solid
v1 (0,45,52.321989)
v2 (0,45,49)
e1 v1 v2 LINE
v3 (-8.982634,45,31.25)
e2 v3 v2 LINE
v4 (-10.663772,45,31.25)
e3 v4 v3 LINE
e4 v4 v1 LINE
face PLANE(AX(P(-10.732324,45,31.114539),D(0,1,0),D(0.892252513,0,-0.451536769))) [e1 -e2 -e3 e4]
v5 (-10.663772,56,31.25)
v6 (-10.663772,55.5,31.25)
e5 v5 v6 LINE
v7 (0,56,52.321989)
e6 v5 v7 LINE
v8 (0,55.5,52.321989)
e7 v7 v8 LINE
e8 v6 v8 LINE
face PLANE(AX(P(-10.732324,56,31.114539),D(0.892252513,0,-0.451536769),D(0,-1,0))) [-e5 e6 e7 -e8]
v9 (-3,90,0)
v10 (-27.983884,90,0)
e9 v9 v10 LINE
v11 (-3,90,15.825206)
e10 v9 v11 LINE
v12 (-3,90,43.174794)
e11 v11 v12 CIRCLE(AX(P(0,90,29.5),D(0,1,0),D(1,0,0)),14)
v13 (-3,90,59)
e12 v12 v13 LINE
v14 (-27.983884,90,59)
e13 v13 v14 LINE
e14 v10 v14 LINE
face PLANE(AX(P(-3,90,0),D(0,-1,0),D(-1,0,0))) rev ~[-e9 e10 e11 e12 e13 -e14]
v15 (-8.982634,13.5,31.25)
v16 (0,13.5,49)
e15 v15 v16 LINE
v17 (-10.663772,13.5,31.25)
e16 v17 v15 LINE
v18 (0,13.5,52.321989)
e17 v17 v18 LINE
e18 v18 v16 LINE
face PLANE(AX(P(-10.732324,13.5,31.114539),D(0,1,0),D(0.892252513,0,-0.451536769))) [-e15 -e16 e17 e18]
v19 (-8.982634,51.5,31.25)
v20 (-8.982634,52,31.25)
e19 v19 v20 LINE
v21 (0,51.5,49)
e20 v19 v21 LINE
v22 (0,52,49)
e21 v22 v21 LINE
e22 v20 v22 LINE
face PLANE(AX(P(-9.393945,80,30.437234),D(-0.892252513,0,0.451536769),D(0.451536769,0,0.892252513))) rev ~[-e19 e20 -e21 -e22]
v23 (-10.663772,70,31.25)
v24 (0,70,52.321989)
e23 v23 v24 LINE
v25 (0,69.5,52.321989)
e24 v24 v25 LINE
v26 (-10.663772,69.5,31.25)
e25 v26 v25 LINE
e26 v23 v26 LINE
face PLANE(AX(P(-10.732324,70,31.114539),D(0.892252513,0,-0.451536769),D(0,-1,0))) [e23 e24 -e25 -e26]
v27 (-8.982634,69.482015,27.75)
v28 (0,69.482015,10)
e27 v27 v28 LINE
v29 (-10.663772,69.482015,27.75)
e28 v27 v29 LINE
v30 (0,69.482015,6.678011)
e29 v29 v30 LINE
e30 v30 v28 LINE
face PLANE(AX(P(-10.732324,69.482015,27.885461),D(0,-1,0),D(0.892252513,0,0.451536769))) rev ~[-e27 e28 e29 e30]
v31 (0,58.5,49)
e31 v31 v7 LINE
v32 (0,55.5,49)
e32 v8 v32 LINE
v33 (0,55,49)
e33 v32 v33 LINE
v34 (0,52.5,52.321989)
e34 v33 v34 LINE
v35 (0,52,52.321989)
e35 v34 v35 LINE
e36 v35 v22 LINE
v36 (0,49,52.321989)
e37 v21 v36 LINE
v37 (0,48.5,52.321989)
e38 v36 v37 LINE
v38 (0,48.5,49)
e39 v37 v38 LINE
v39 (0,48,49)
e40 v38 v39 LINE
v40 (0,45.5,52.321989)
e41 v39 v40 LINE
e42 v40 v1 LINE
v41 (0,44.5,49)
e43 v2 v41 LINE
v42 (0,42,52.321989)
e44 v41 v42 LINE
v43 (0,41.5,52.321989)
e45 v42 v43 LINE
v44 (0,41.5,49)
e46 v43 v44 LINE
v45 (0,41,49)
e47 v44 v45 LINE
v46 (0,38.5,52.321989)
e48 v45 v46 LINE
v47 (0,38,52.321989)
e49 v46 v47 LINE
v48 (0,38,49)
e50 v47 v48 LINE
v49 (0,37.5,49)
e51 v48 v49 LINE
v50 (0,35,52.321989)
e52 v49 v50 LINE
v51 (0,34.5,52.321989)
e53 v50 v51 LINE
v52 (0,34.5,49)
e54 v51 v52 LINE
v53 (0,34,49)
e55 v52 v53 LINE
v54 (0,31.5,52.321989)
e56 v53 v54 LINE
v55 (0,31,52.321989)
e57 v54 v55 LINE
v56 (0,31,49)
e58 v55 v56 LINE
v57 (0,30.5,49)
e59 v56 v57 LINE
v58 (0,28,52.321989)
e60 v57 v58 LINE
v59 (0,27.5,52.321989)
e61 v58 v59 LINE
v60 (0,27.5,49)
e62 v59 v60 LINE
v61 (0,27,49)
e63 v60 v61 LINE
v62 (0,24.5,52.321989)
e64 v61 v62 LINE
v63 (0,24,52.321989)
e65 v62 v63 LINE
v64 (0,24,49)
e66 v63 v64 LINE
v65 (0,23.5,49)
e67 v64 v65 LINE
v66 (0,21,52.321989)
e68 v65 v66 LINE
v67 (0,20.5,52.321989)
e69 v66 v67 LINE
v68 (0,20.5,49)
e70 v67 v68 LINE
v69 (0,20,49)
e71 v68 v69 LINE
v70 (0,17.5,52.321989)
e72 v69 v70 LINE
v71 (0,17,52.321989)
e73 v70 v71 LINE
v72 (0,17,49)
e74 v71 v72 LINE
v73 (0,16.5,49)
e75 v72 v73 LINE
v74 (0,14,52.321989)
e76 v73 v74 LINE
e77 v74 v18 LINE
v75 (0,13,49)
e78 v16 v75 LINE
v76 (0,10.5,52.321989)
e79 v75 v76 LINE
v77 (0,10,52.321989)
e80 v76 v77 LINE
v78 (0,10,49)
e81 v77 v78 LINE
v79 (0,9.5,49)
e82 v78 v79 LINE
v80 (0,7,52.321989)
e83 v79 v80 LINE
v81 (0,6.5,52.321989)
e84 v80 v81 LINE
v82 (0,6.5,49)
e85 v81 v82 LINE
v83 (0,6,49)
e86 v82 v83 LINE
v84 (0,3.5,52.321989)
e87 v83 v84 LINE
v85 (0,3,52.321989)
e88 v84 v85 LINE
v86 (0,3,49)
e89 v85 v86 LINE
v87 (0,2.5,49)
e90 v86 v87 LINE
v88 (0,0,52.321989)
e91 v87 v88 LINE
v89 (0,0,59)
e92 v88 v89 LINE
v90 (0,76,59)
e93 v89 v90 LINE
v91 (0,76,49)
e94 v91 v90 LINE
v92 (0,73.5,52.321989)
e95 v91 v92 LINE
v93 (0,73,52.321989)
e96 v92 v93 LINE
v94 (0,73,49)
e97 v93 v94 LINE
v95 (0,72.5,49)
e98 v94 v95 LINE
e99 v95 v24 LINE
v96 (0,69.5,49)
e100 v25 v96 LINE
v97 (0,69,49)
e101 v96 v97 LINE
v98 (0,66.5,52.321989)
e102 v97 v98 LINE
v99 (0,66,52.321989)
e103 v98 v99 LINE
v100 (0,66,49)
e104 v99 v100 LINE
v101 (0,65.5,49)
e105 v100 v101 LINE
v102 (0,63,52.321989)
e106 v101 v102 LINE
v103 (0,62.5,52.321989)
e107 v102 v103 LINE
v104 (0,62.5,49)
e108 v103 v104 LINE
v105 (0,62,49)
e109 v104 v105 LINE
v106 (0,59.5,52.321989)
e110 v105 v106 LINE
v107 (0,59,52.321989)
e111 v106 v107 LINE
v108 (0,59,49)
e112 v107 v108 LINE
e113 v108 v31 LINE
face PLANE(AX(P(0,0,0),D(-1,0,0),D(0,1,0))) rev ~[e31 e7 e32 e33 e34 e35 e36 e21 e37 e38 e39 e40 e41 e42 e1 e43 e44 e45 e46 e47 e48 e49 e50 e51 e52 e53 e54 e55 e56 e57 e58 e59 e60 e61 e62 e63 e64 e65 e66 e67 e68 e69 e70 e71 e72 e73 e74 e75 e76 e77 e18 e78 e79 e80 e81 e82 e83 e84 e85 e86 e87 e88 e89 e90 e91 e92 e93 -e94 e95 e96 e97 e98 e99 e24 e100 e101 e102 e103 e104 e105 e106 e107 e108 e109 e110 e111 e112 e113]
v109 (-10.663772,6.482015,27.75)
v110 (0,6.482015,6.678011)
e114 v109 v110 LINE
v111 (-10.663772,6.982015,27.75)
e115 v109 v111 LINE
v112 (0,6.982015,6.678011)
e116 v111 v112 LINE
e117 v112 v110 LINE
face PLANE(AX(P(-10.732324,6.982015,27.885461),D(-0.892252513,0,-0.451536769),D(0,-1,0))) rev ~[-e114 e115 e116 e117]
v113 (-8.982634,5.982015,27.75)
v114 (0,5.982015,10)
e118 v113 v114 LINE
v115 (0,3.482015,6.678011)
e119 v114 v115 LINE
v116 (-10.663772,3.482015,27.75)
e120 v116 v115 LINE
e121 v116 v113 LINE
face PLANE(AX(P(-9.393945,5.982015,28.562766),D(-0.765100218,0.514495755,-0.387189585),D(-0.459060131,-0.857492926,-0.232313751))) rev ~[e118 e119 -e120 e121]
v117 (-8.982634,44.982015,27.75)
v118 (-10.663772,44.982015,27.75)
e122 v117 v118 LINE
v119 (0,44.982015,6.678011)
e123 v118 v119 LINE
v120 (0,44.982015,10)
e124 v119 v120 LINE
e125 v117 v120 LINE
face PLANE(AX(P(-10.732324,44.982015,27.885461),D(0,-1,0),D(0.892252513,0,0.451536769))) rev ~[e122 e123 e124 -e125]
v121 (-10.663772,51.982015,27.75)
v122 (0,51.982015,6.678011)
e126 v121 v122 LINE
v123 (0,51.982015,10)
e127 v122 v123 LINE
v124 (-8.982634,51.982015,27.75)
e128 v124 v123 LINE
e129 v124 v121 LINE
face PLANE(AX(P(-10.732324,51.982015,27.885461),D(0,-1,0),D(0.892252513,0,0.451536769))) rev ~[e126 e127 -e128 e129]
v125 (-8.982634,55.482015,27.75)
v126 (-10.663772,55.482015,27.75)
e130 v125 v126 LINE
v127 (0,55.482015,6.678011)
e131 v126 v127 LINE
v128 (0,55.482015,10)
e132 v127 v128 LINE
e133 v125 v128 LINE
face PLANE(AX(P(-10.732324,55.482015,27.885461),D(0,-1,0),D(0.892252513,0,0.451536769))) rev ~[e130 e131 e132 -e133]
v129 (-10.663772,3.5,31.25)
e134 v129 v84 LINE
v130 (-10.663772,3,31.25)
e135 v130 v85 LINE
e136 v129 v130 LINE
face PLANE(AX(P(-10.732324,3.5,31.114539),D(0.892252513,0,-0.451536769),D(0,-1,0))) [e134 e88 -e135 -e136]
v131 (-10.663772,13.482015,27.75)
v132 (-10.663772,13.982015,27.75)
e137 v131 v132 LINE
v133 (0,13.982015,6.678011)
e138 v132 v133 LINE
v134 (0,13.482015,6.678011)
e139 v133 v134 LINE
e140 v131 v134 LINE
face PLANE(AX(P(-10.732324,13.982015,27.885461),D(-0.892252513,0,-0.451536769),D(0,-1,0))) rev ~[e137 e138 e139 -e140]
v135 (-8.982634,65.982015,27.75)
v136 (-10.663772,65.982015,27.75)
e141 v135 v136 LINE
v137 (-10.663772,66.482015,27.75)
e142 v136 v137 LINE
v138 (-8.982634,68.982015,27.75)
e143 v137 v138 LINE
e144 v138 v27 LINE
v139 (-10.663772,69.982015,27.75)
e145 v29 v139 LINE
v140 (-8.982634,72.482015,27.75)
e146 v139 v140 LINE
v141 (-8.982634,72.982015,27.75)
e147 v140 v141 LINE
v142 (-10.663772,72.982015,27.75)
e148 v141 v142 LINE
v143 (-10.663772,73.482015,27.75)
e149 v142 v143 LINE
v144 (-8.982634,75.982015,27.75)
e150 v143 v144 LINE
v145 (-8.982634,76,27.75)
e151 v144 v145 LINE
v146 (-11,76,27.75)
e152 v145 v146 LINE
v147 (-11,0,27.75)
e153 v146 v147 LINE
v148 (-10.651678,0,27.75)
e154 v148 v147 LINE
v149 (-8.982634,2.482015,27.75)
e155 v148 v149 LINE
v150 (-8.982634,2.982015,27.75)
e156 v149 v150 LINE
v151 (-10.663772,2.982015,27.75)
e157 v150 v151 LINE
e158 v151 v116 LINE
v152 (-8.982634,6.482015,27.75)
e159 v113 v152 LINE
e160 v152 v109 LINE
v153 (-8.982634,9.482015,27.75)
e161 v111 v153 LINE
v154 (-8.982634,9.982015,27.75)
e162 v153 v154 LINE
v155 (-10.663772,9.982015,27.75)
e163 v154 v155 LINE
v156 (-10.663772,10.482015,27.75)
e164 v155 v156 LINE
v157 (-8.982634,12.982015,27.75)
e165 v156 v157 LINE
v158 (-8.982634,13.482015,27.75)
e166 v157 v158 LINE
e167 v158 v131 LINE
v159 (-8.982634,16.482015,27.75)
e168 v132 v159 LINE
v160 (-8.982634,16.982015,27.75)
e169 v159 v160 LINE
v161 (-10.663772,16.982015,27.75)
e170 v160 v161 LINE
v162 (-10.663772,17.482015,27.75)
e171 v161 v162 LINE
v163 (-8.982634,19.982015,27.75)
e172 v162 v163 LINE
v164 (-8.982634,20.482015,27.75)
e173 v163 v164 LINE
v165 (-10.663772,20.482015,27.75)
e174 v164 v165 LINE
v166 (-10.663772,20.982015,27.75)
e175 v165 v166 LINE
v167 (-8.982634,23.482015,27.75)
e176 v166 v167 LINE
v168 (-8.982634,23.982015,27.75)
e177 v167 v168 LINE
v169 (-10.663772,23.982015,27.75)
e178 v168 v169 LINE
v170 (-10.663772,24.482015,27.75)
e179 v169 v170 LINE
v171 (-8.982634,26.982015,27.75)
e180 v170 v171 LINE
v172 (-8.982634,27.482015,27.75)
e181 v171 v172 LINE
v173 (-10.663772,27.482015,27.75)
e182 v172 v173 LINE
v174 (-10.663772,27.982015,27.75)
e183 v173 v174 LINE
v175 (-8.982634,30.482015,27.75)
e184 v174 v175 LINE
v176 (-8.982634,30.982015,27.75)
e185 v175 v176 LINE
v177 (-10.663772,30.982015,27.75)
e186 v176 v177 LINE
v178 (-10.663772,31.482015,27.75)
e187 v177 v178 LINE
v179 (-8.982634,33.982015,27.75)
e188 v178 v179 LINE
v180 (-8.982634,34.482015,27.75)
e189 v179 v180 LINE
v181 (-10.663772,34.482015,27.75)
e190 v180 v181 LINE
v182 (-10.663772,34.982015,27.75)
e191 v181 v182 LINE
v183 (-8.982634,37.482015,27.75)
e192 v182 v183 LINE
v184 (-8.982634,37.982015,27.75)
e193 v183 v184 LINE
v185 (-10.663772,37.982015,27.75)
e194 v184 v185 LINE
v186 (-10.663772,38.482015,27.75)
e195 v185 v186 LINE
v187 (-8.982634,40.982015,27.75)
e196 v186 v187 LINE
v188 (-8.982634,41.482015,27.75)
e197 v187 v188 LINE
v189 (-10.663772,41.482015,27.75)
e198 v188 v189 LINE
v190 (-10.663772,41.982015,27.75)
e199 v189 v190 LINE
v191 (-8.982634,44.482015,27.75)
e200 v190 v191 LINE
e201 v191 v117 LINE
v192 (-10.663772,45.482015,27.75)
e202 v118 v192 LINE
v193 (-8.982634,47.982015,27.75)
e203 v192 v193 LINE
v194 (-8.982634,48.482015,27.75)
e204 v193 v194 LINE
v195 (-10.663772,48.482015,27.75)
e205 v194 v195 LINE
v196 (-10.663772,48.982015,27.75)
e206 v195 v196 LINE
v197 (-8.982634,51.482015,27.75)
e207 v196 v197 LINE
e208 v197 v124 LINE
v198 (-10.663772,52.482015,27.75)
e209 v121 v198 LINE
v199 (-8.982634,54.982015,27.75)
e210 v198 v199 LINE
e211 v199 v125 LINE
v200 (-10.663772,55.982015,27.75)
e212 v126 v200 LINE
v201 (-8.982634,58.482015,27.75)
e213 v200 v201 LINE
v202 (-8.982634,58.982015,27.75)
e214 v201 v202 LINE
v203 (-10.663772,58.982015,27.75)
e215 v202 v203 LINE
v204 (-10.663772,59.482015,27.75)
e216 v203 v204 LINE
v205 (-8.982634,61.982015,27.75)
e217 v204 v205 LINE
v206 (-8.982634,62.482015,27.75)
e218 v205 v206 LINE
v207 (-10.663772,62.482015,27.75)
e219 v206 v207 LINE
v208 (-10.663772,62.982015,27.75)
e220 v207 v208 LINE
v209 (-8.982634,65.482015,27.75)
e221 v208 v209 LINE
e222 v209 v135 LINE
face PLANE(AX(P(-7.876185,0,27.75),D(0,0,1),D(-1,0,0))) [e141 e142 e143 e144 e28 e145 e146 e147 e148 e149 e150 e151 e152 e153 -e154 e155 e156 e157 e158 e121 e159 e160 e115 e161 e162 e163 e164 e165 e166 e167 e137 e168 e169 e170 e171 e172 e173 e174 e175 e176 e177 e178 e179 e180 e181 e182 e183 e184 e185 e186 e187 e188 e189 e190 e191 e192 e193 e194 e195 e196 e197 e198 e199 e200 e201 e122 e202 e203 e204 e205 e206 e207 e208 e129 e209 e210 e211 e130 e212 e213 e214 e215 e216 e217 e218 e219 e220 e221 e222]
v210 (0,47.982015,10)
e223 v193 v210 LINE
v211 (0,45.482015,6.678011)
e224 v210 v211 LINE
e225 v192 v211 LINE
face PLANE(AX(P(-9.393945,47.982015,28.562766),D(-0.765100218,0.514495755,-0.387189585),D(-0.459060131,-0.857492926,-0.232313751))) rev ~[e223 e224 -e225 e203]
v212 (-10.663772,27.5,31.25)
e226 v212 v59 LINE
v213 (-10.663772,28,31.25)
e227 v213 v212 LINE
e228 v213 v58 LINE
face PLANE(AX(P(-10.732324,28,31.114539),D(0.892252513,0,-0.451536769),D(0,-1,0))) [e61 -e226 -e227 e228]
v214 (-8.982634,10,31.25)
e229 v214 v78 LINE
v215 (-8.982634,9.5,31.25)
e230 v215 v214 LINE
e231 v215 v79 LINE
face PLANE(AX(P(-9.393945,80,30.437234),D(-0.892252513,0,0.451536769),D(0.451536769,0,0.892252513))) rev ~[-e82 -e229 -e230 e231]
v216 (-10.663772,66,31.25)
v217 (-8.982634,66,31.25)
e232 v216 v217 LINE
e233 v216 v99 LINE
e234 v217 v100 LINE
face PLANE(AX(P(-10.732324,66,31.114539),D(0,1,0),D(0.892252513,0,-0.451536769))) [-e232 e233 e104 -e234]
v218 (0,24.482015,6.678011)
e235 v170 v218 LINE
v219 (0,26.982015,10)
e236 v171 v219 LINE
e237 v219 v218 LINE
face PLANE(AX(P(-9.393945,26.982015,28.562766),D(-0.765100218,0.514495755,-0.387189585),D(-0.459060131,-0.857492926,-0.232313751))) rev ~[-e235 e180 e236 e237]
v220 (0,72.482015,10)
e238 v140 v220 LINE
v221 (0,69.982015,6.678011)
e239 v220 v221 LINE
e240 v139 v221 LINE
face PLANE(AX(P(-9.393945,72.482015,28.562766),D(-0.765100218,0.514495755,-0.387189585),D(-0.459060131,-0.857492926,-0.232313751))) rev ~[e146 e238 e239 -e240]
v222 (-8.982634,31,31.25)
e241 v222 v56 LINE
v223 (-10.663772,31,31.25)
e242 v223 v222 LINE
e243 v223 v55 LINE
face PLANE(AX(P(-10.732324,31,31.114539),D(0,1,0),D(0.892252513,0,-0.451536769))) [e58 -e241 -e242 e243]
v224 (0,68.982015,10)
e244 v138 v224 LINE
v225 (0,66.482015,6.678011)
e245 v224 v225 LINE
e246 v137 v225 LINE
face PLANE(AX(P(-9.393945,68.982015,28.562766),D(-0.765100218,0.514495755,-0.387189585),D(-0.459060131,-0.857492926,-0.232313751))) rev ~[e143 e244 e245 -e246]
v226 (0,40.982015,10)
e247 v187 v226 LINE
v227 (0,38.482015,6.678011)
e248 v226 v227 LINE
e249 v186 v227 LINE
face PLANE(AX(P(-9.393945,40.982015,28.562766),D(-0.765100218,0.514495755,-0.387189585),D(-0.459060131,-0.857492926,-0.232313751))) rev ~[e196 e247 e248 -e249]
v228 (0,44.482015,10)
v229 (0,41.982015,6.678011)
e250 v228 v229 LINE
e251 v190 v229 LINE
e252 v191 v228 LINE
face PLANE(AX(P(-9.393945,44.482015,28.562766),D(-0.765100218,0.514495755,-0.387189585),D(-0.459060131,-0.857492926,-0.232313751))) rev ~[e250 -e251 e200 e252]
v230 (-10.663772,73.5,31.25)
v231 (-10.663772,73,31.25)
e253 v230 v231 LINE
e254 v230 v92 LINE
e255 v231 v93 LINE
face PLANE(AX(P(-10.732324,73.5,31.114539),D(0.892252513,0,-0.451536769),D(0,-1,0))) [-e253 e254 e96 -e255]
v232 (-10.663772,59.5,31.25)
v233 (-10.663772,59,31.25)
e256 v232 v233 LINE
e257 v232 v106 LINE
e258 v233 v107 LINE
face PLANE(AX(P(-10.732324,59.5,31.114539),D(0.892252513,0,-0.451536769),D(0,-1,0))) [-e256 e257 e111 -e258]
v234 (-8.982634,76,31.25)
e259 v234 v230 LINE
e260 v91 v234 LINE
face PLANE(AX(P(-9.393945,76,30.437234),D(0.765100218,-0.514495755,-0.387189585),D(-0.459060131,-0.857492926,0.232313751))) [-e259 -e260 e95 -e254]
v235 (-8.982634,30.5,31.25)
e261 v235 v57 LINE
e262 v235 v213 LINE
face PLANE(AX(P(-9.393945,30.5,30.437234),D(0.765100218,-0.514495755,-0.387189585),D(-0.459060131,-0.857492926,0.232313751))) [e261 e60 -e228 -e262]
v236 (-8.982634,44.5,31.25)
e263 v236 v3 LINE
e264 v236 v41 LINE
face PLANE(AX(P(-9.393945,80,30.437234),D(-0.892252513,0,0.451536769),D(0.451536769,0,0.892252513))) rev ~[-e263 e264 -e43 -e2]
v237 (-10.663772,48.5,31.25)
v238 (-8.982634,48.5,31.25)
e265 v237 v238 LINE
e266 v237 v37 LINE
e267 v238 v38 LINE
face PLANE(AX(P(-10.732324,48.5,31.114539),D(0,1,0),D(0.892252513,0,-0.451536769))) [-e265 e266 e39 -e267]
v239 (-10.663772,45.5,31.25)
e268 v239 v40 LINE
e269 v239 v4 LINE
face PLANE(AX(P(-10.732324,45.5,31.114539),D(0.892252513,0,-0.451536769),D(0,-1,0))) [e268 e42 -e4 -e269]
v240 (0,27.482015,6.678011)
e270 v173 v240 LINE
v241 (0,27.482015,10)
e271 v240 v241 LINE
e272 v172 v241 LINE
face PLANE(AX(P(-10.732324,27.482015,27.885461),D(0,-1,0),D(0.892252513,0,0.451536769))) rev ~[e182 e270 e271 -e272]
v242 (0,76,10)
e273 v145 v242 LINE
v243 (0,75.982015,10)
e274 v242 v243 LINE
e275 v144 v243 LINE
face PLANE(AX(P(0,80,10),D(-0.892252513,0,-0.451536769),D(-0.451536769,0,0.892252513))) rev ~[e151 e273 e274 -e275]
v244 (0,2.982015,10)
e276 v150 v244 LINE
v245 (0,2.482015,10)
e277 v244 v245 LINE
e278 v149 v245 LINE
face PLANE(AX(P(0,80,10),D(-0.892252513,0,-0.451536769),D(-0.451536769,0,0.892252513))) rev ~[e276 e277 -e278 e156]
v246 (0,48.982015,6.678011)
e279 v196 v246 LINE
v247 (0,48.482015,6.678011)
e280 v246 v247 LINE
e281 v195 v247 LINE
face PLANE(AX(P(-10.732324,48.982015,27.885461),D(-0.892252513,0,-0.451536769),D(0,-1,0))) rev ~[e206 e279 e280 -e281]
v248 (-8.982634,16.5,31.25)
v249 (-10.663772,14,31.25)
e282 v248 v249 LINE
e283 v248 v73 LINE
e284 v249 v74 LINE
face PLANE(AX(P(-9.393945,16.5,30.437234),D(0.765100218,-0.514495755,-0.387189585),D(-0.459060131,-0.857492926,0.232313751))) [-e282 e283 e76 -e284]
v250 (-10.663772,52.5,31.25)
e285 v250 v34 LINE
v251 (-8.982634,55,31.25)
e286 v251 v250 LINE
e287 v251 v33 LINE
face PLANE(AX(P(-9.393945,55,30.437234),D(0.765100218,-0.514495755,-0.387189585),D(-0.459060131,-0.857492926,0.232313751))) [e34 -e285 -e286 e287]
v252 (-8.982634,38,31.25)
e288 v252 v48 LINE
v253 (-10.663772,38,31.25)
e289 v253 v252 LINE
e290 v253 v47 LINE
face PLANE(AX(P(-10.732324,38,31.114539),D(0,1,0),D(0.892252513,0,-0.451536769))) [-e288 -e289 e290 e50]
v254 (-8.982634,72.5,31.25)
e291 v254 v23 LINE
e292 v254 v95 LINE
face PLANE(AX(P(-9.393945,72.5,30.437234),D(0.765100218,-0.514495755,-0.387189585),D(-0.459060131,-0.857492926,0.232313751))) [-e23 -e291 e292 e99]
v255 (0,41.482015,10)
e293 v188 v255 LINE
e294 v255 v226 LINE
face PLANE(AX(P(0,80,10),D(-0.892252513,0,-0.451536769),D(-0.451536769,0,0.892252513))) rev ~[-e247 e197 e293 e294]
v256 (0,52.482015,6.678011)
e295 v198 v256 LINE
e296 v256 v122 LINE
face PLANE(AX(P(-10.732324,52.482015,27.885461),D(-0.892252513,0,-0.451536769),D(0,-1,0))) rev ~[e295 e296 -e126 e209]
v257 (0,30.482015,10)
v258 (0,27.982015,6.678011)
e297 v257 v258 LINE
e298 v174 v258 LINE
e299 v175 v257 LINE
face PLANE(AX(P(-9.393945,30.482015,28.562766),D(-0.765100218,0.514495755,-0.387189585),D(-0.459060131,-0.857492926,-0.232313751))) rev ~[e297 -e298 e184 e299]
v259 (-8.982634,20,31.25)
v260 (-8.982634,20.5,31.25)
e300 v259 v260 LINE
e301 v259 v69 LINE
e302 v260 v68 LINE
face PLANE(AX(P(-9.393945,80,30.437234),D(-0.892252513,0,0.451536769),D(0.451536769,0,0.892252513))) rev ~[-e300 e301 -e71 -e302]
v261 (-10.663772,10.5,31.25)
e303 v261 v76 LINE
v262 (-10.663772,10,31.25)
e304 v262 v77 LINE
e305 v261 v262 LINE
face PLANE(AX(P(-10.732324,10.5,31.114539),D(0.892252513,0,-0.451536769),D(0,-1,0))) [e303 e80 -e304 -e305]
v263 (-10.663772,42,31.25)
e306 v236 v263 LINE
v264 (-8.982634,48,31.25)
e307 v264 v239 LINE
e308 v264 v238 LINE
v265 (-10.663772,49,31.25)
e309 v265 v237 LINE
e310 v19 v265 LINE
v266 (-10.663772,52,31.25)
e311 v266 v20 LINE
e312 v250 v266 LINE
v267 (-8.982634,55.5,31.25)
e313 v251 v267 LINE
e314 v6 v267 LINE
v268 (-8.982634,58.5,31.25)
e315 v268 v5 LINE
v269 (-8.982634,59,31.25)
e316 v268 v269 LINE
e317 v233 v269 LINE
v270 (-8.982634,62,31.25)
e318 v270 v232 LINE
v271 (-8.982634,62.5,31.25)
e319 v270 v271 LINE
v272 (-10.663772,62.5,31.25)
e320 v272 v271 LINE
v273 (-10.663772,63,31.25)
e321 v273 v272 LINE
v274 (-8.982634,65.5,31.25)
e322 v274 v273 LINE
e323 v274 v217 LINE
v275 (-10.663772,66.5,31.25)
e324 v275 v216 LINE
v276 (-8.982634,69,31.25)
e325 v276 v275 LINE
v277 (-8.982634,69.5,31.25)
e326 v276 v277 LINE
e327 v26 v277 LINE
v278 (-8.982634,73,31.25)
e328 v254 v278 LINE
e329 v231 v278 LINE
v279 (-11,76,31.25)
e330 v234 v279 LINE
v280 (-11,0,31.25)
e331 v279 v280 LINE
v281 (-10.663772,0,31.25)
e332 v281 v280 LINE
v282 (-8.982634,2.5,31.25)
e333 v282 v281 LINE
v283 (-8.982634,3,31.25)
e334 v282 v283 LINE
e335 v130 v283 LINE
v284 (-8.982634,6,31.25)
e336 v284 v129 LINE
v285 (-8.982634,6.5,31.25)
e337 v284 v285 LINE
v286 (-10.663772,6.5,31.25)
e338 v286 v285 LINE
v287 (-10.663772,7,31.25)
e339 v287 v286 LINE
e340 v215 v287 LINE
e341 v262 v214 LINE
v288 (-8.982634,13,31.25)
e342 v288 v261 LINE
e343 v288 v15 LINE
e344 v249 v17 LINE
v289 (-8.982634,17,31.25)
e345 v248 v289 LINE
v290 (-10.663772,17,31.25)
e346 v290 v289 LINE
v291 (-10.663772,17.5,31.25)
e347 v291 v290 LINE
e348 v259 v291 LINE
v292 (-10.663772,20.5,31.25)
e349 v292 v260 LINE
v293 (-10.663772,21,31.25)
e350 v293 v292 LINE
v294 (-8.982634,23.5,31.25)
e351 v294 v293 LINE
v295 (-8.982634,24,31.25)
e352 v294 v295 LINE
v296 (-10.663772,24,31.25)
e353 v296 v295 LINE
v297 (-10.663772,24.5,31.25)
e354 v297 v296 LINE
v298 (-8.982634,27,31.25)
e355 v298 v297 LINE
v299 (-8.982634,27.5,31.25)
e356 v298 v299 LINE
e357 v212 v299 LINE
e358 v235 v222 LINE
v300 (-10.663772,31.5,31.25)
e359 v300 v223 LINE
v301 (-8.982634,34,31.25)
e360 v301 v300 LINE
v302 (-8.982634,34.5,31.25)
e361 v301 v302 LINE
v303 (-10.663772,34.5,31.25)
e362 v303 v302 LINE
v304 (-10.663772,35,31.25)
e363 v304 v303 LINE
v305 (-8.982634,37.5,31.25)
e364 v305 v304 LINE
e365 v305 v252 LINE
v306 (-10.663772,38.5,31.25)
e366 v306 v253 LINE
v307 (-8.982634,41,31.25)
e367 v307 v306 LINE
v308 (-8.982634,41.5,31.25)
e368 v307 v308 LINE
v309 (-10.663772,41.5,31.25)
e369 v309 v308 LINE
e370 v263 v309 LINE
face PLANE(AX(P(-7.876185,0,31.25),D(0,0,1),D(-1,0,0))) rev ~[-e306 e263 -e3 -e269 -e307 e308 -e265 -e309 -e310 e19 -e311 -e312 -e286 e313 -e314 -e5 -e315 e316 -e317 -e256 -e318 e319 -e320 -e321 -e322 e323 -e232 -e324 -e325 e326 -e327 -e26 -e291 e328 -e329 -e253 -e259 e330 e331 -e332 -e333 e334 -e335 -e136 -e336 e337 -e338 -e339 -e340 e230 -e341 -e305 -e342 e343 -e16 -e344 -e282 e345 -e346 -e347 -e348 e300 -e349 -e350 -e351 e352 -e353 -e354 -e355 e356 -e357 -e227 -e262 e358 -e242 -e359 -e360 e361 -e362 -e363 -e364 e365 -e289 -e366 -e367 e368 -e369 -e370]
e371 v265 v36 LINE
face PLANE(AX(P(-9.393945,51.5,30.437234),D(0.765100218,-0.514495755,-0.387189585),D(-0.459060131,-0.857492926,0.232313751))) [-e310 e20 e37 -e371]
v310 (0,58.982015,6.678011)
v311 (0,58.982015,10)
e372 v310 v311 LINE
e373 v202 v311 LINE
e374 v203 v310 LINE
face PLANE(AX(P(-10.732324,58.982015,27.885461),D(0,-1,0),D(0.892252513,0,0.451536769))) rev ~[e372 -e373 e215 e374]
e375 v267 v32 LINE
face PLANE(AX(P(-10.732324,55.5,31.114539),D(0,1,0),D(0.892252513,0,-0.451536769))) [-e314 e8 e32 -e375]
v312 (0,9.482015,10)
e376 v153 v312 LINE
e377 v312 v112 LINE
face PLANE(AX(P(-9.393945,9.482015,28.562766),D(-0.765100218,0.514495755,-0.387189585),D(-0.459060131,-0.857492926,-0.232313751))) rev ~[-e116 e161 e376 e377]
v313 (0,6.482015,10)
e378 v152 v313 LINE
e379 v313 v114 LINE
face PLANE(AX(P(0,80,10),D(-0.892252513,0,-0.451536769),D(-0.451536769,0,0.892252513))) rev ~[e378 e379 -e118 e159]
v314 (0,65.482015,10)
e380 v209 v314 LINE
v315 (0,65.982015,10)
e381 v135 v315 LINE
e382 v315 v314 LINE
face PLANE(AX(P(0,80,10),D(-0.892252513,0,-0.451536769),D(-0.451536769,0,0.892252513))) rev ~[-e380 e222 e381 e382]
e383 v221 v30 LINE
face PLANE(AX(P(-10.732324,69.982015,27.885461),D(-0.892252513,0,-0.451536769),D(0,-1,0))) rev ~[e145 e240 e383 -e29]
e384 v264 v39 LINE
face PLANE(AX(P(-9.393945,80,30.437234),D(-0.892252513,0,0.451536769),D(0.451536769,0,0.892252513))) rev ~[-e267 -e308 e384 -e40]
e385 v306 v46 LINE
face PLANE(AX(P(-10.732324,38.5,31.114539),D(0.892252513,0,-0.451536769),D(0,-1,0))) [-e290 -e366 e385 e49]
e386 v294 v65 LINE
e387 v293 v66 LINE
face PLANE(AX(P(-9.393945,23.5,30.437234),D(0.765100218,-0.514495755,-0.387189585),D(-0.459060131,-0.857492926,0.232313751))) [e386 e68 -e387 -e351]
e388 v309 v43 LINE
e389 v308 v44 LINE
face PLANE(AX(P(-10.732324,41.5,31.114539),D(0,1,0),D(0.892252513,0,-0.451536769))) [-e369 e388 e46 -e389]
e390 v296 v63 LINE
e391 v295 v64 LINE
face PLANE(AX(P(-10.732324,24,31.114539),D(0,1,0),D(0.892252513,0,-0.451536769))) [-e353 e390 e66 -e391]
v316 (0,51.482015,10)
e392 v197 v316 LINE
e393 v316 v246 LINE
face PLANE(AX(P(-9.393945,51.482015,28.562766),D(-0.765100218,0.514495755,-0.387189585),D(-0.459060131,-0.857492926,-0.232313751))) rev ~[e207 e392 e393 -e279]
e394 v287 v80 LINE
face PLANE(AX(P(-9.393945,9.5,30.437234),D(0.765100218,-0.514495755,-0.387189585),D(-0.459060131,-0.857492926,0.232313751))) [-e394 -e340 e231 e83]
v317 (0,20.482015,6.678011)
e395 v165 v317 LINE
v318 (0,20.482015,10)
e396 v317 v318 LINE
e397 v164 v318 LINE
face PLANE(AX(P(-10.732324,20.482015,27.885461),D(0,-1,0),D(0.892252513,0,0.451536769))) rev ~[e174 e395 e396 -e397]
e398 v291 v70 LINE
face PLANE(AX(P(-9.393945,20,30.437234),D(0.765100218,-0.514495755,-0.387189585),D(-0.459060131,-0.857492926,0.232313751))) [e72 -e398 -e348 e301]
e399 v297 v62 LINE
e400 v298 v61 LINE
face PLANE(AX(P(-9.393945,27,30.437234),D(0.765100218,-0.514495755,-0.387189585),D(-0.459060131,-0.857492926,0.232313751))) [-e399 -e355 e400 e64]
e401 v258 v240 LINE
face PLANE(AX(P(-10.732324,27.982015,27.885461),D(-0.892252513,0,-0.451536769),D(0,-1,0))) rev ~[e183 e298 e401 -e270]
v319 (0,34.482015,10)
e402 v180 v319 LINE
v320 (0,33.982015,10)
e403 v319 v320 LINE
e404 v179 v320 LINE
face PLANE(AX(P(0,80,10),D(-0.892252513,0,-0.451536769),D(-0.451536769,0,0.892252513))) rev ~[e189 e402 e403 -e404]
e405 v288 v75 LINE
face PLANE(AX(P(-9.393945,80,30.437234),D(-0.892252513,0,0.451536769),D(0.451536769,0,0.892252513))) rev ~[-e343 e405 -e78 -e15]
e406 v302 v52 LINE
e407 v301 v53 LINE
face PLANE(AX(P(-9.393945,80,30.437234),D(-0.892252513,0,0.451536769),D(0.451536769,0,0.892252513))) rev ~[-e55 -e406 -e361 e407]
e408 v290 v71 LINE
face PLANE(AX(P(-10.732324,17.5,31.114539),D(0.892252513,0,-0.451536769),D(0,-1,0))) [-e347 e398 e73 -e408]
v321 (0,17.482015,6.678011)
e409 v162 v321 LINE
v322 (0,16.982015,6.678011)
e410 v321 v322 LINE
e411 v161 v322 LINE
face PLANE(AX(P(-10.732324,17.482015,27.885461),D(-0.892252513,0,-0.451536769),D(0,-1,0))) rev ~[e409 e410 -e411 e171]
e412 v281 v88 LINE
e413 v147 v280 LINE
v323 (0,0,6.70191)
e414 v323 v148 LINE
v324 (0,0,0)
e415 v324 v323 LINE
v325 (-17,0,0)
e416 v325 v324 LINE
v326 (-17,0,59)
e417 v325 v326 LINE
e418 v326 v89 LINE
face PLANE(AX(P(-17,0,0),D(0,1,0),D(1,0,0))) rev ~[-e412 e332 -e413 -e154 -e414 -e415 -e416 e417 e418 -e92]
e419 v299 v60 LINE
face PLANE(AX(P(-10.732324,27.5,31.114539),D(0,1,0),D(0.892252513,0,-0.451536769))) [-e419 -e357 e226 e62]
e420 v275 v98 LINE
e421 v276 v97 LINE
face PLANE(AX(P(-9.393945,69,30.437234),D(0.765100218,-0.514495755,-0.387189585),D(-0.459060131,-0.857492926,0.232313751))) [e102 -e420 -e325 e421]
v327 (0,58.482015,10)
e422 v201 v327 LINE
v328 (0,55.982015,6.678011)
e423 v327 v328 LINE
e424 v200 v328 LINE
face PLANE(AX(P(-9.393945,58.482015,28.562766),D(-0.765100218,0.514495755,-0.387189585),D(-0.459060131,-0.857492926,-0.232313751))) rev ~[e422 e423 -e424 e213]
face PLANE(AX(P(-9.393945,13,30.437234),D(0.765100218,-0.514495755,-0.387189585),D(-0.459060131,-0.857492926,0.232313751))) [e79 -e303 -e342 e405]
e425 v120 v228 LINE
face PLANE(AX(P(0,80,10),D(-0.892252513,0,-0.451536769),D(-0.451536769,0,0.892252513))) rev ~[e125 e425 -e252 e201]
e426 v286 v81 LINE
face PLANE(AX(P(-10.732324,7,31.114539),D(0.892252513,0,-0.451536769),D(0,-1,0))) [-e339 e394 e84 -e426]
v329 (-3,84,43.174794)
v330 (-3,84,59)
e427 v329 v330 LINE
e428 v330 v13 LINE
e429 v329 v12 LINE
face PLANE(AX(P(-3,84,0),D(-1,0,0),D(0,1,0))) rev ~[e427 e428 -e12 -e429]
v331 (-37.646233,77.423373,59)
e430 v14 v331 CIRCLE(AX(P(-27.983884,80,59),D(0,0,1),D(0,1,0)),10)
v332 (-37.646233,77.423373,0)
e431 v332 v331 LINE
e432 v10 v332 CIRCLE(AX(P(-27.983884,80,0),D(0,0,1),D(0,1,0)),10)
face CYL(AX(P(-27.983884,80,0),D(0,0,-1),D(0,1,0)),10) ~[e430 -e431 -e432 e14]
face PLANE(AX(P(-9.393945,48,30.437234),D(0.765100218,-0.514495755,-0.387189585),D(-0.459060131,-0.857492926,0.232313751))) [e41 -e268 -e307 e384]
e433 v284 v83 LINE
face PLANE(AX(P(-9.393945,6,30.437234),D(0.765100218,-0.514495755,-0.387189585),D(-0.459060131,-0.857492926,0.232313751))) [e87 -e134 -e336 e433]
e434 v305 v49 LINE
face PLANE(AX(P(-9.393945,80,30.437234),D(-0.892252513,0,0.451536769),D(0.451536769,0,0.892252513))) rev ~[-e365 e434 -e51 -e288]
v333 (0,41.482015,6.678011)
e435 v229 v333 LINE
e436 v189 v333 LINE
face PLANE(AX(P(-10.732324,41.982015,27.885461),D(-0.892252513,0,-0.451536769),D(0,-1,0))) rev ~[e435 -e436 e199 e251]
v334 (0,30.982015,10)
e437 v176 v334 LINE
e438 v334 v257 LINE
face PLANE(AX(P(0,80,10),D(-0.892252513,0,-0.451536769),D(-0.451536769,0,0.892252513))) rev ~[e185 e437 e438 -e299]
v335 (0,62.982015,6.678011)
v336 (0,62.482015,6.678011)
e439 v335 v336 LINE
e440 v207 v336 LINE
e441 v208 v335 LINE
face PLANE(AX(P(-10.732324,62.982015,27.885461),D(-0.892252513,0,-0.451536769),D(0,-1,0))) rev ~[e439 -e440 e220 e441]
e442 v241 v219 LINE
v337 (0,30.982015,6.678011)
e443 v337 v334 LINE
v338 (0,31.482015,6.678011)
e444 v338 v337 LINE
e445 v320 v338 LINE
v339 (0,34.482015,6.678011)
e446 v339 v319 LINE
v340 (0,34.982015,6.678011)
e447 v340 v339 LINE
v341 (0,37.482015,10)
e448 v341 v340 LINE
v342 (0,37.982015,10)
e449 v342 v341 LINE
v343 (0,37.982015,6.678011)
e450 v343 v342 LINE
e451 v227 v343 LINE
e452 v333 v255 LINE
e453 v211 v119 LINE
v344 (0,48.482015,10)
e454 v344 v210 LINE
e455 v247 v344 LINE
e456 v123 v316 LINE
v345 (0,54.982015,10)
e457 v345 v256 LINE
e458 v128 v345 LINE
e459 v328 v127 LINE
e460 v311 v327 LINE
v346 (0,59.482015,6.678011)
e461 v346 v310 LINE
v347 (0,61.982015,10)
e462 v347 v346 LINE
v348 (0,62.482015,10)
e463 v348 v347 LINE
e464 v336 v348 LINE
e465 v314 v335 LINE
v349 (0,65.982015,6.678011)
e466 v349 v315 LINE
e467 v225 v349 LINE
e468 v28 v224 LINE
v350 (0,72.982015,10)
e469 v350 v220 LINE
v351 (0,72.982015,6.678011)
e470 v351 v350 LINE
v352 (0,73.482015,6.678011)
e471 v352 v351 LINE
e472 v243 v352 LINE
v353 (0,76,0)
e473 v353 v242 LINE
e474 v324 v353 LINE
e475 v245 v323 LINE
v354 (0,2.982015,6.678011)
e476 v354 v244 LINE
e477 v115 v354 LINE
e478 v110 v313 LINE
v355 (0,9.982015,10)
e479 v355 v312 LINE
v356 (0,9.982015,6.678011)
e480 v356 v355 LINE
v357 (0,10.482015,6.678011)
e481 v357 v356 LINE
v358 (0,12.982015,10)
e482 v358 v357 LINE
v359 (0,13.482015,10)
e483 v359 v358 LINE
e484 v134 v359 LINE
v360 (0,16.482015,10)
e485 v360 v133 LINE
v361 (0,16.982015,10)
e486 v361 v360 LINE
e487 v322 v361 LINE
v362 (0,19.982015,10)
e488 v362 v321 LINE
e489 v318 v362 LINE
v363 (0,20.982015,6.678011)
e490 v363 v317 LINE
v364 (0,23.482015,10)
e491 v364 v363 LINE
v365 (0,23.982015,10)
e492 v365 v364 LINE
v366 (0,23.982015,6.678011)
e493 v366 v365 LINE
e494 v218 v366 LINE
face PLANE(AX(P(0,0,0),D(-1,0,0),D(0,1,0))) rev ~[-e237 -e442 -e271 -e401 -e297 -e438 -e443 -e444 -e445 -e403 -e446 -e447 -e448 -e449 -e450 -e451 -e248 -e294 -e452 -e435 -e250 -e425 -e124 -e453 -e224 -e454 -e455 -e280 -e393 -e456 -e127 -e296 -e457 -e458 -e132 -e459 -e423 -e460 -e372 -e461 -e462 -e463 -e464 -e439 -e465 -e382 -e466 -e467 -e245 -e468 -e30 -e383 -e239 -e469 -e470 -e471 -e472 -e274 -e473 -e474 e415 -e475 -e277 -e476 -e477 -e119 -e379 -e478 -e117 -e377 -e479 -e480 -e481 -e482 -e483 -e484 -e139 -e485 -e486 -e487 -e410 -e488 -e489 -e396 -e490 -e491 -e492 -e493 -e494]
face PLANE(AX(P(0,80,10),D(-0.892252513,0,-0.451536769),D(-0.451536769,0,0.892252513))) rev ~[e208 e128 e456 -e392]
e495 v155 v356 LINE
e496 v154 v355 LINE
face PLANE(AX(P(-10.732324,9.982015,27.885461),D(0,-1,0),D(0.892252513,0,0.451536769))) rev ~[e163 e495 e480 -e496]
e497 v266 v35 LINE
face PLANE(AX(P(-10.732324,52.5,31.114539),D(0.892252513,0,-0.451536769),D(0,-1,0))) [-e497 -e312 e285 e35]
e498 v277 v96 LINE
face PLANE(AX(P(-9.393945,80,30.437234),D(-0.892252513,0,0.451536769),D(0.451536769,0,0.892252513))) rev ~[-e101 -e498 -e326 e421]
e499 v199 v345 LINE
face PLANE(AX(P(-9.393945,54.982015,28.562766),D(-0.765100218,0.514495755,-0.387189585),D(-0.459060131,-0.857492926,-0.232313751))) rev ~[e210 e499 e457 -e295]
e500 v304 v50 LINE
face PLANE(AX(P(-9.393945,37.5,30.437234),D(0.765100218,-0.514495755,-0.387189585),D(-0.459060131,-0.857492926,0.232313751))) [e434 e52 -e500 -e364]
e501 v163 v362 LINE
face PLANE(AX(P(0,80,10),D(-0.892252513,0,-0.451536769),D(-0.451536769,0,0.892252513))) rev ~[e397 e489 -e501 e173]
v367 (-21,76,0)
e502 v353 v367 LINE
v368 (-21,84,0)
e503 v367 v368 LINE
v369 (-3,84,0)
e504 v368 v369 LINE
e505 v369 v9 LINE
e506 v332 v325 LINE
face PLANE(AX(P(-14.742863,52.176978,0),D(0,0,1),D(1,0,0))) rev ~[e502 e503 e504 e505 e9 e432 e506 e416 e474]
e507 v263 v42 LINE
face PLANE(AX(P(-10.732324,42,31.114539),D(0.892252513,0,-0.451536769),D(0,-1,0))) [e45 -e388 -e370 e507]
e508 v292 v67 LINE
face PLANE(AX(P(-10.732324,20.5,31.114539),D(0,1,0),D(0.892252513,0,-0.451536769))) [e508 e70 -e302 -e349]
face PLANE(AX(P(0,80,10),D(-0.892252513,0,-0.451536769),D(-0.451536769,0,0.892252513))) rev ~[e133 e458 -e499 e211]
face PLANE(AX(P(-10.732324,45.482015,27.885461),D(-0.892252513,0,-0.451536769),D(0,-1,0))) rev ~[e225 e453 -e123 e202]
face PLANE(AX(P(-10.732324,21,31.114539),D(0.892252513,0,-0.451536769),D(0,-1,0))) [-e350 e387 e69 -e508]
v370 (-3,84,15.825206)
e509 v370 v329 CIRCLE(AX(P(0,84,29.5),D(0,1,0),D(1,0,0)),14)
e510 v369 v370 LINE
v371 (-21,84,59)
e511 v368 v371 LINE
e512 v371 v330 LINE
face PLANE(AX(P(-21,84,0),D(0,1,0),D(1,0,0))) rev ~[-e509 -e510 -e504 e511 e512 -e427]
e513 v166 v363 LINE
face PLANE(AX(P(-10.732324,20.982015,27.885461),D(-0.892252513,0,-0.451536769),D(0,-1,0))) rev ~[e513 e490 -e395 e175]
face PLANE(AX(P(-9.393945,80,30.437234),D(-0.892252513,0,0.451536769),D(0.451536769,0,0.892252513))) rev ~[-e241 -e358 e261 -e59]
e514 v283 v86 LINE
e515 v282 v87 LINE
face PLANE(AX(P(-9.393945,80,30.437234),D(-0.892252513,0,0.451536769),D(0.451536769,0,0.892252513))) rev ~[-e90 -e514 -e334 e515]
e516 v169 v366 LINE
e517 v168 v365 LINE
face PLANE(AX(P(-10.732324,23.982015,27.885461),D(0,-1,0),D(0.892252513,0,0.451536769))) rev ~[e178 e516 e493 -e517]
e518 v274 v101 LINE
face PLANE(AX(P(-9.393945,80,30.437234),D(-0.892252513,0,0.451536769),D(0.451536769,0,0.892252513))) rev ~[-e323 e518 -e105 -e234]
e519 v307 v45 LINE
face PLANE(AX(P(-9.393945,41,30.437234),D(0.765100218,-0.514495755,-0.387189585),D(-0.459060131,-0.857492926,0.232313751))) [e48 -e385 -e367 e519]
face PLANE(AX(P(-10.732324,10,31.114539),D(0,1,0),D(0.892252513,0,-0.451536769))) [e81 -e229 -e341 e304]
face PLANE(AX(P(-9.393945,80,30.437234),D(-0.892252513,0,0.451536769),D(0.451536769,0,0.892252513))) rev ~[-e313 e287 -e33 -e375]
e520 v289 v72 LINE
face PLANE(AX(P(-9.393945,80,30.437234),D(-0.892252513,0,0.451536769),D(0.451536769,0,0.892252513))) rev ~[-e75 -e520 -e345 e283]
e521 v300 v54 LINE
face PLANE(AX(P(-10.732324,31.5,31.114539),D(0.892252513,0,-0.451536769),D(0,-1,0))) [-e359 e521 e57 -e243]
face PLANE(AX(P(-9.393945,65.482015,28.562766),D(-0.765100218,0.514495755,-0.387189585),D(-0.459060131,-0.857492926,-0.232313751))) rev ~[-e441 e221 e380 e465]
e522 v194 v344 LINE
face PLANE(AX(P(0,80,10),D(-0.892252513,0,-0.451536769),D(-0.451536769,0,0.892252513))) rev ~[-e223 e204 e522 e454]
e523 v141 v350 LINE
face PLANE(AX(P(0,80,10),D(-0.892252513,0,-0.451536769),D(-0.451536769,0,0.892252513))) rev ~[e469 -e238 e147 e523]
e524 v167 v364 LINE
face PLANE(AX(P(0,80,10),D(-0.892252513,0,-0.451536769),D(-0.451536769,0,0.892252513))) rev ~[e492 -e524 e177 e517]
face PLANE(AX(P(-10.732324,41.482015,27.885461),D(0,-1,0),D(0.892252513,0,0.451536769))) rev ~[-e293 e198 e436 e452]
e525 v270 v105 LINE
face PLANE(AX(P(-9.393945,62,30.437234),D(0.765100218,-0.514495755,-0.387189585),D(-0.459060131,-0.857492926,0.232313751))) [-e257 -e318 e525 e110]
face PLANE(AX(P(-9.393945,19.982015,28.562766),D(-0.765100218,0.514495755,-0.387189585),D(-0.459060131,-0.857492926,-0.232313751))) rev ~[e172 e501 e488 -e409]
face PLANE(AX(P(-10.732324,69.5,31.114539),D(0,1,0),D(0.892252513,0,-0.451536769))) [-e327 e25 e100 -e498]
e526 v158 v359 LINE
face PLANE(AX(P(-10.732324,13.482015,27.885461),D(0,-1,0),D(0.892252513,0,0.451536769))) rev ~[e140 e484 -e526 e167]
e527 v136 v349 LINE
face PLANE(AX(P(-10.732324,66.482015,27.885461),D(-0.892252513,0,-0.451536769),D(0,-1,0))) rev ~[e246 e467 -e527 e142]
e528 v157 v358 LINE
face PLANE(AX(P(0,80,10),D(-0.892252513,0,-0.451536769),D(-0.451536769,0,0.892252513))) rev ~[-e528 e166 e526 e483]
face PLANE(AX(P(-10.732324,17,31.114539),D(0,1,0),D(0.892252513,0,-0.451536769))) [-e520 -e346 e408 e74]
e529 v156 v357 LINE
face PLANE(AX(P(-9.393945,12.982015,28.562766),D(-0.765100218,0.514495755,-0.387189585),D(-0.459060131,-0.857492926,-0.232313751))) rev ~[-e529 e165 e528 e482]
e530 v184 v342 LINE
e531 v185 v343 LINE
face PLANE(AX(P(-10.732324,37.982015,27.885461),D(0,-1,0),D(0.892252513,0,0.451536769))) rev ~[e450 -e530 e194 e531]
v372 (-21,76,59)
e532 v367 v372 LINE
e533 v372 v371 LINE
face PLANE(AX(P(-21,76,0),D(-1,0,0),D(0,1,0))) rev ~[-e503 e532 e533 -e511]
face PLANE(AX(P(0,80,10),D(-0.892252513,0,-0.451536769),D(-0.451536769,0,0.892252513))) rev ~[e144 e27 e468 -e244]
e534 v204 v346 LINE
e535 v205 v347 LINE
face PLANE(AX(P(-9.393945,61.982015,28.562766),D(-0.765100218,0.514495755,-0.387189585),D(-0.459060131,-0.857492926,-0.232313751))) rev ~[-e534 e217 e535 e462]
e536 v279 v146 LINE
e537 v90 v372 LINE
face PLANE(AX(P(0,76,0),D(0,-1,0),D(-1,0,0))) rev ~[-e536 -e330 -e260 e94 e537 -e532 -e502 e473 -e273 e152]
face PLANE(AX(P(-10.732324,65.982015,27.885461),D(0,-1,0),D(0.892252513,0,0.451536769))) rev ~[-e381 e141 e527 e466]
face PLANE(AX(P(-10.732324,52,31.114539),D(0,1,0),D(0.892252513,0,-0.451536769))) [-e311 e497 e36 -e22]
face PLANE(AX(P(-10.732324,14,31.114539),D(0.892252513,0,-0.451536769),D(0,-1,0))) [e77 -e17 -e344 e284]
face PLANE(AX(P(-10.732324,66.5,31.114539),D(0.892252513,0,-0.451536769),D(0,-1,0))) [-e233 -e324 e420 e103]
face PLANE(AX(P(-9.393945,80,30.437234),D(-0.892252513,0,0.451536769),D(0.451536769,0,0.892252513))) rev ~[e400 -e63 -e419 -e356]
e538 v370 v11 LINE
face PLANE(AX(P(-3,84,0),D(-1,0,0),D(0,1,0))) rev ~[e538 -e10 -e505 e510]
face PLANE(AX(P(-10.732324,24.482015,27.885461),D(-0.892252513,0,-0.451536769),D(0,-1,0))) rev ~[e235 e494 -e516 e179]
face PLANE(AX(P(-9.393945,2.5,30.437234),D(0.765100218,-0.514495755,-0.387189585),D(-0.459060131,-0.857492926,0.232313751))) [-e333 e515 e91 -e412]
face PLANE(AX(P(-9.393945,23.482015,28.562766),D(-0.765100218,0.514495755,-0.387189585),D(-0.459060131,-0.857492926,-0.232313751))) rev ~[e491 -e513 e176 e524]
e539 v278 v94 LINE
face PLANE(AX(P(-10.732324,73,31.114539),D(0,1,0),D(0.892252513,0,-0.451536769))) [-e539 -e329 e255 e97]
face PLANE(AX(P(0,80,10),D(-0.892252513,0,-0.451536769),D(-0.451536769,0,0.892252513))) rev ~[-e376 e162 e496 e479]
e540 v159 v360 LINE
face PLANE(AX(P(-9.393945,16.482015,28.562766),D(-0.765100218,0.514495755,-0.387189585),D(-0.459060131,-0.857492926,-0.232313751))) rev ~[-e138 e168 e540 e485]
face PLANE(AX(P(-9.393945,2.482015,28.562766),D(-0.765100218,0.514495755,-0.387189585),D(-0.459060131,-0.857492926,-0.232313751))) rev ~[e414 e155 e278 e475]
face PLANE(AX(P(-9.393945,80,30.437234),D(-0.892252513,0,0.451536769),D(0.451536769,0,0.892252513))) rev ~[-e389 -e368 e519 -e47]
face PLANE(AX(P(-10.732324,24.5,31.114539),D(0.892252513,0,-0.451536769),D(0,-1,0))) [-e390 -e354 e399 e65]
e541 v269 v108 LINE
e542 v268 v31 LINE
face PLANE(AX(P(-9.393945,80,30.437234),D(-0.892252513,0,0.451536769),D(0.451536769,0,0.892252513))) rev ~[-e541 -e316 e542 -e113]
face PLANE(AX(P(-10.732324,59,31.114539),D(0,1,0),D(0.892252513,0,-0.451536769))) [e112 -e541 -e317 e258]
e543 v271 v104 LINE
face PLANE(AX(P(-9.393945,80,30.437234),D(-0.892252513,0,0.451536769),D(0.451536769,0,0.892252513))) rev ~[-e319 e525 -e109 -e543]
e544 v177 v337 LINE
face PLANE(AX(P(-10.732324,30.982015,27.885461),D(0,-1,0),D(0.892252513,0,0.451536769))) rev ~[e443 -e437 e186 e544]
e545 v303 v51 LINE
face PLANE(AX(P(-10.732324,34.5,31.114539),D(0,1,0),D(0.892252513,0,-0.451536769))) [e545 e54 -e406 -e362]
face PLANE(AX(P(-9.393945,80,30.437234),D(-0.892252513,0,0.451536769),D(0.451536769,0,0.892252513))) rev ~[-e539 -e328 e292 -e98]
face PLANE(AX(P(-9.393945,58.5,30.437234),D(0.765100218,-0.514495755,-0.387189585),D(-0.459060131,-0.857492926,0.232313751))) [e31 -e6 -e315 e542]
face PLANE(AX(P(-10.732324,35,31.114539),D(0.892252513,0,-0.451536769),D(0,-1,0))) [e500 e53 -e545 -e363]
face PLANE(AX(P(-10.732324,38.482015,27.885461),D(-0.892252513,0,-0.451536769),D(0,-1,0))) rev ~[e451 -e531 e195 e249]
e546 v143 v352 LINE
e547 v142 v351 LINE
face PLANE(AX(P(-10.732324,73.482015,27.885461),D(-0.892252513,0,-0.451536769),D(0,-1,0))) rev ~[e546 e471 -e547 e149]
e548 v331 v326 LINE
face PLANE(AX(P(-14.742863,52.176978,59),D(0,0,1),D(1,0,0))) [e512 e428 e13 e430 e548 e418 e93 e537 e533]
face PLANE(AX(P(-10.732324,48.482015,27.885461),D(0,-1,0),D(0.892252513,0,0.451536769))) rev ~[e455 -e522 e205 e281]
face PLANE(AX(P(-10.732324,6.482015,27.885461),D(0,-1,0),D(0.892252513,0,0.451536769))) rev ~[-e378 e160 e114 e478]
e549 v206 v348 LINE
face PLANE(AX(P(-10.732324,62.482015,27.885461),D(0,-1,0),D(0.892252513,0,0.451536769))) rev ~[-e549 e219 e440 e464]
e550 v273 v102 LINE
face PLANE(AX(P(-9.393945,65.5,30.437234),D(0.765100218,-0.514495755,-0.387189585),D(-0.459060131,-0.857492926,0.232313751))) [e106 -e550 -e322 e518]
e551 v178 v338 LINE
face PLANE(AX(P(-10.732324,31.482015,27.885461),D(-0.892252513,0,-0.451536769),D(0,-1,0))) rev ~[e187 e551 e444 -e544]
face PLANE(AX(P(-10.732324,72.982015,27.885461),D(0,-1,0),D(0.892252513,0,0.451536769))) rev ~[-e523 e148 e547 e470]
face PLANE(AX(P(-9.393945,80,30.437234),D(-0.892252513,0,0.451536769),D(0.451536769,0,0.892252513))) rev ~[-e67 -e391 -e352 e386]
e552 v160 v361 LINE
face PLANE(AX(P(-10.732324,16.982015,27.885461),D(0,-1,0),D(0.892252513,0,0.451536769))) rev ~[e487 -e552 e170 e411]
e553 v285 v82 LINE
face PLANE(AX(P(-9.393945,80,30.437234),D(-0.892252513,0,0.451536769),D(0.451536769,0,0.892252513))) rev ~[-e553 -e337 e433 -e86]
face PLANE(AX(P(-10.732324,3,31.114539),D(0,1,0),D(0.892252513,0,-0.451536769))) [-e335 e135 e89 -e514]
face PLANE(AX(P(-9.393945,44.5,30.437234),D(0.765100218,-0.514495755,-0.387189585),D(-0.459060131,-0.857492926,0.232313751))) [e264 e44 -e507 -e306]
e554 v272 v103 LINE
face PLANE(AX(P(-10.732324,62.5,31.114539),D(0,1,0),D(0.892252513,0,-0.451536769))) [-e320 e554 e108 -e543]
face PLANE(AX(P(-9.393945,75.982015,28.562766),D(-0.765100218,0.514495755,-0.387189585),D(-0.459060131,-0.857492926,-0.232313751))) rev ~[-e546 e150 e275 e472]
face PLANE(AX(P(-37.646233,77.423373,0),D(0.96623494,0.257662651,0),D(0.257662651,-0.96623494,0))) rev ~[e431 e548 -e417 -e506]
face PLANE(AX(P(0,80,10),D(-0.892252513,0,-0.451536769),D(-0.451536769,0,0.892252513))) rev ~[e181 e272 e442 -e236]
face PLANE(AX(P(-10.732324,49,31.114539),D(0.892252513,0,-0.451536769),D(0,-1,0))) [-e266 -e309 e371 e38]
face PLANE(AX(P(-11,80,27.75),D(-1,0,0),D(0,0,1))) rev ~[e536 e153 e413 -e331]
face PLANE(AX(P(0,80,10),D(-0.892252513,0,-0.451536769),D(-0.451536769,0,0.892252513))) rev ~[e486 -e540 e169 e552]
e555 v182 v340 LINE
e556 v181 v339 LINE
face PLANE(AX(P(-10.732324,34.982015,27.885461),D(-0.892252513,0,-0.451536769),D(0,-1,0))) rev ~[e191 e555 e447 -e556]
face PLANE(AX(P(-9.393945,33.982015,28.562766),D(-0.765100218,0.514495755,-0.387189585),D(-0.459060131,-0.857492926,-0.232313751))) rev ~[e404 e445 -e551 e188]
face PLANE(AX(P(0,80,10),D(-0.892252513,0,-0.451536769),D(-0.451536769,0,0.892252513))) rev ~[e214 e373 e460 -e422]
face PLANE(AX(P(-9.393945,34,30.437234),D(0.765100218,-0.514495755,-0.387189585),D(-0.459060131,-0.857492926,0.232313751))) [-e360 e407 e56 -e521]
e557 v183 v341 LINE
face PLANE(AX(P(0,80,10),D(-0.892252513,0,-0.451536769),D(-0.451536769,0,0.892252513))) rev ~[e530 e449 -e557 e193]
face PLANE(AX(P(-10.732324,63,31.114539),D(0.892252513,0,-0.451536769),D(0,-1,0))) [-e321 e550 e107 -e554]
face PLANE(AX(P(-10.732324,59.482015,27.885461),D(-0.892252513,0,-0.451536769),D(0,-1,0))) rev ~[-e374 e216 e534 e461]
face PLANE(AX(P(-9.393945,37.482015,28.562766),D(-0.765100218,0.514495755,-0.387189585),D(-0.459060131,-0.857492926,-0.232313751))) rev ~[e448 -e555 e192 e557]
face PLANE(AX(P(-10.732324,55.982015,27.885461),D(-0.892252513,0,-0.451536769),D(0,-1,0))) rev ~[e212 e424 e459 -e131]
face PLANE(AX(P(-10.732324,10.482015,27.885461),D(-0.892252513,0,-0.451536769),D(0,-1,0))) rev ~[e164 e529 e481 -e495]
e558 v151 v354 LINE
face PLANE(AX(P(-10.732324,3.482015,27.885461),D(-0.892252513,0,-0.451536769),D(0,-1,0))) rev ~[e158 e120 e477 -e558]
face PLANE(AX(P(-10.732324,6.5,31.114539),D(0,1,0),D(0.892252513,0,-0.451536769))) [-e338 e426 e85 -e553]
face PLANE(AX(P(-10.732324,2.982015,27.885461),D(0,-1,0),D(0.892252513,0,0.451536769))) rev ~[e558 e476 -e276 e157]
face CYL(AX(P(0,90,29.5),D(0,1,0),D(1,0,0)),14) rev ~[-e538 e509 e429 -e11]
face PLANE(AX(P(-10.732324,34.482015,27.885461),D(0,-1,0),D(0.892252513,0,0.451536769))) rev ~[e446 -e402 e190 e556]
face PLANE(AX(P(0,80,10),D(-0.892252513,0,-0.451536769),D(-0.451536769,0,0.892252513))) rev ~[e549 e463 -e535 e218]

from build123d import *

# Parameters (mm, degrees)
BOSS_EXTRUDE1_DEPTH     = 59
CUT_EXTRUDE2_REACH      = 116.122
SKETCH3_R               = 14
CUT_EXTRUDE3_DEPTH      = 115.121756946
CUT_EXTRUDE3_DEPTH_BACK = 80
CUT_EXTRUDE5_DEPTH      = 80
CUT_EXTRUDE6_DEPTH      = 99.782303331
SKETCH9_W               = 3.123815153
SKETCH9_H               = 3.5
CUT_EXTRUDE7_DEPTH      = 80


with BuildPart() as part:
    # Sketch1 → Boss-Extrude1 (new body)
    with BuildSketch(Plane.XY):
        with BuildLine():
            Line((0, 0), (0, 76))
            Line((0, 76), (-21, 76))
            Line((-21, 76), (-21, 84))
            Line((-21, 84), (-3, 84))
            Line((-3, 84), (-3, 90))
            Line((-3, 90), (-27.983883536, 90))
            ThreePointArc((-27.983883536, 90), (-35.913772093, 86.092361404), (-37.646232932, 77.423373494))
            Line((-37.646232932, 77.423373494), (-17, 0))
            Line((-17, 0), (0, 0))
        make_face()
    extrude(amount=BOSS_EXTRUDE1_DEPTH)

    # Sketch3 → Cut-Extrude2 (cut, up to next)
    with BuildSketch(Plane(origin=(0, 90, 0), x_dir=(1, 0, 0), z_dir=(0, 1, 0)), mode=Mode.PRIVATE) as cut_extrude2_sk1:
        with Locations((0, -29.5)):
            Circle(SKETCH3_R)
    cut_extrude2_tool1 = extrude(cut_extrude2_sk1.sketch, amount=-CUT_EXTRUDE2_REACH, mode=Mode.PRIVATE) & part.part
    add(cut_extrude2_tool1.solids().sort_by_distance((0, 90, 29.5))[0], mode=Mode.SUBTRACT)

    # Sketch4 → Cut-Extrude3 (cut, two sides: drawn at the far end of the back side and taken through both)
    with BuildSketch(Plane(origin=(0, 0, 0), x_dir=(-1, 0, 0), z_dir=(0, -1, 0)).offset(-CUT_EXTRUDE3_DEPTH_BACK)):
        Polygon((9.393945477, -30.437233817), (0, -49), (0, -10), (9.393945477, -28.562766183), (11, -27.75), (11, -31.25), align=None)
    extrude(amount=CUT_EXTRUDE3_DEPTH + CUT_EXTRUDE3_DEPTH_BACK, mode=Mode.SUBTRACT)

    # Sketch7 → Cut-Extrude5 (cut)
    with BuildSketch(Plane(origin=(10.347410524, 0, 20.446846604), x_dir=(-0.8922525128420106, 0, 0.45153676852180913), z_dir=(-0.4515367685218092, 0, -0.8922525128420107))):
        Polygon((22.125301658, 2.5), (23.625301658, 0), (21.086592601, -2.199739596), (20.043900458, 77.689978498), (22.125301658, 76.5), (22.125301658, 76), (23.625301658, 73.5), (23.625301658, 73), (22.125301658, 73), (22.125301658, 72.5), (23.625301658, 70), (23.625301658, 69.5), (22.125301658, 69.5), (22.125301658, 69), (23.625301658, 66.5), (23.625301658, 66), (22.125301658, 66), (22.125301658, 65.5), (23.625301658, 63), (23.625301658, 62.5), (22.125301658, 62.5), (22.125301658, 62), (23.625301658, 59.5), (23.625301658, 59), (22.125301658, 59), (22.125301658, 58.5), (23.625301658, 56), (23.625301658, 55.5), (22.125301658, 55.5), (22.125301658, 55), (23.625301658, 52.5), (23.625301658, 52), (22.125301658, 52), (22.125301658, 51.5), (23.625301658, 49), (23.625301658, 48.5), (22.125301658, 48.5), (22.125301658, 48), (23.625301658, 45.5), (23.625301658, 45), (22.125301658, 45), (22.125301658, 44.5), (23.625301658, 42), (23.625301658, 41.5), (22.125301658, 41.5), (22.125301658, 41), (23.625301658, 38.5), (23.625301658, 38), (22.125301658, 38), (22.125301658, 37.5), (23.625301658, 35), (23.625301658, 34.5), (22.125301658, 34.5), (22.125301658, 34), (23.625301658, 31.5), (23.625301658, 31), (22.125301658, 31), (22.125301658, 30.5), (23.625301658, 28), (23.625301658, 27.5), (22.125301658, 27.5), (22.125301658, 27), (23.625301658, 24.5), (23.625301658, 24), (22.125301658, 24), (22.125301658, 23.5), (23.625301658, 21), (23.625301658, 20.5), (22.125301658, 20.5), (22.125301658, 20), (23.625301658, 17.5), (23.625301658, 17), (22.125301658, 17), (22.125301658, 16.5), (23.625301658, 14), (23.625301658, 13.5), (22.125301658, 13.5), (22.125301658, 13), (23.625301658, 10.5), (23.625301658, 10), (22.125301658, 10), (22.125301658, 9.5), (23.625301658, 7), (23.625301658, 6.5), (22.125301658, 6.5), (22.125301658, 6), (23.625301658, 3.5), (23.625301658, 3), (22.125301658, 3), align=None)
    extrude(amount=-CUT_EXTRUDE5_DEPTH, mode=Mode.SUBTRACT)

    # Sketch8 → Cut-Extrude6 (cut, through all)
    with BuildSketch(Plane(origin=(-13.42279364, 0, 26.52391165), x_dir=(0.8922525128420106, 0, 0.45153676852180913), z_dir=(-0.4515367685218092, 0, 0.8922525128420107))):
        Polygon((6.596768885, 77.671993362), (4.515367685, 76.482014864), (4.515367685, 75.982014864), (3.015367685, 73.482014864), (3.015367685, 72.982014864), (4.515367685, 72.982014864), (4.515367685, 72.482014864), (3.015367685, 69.982014864), (3.015367685, 69.482014864), (4.515367685, 69.482014864), (4.515367685, 68.982014864), (3.015367685, 66.482014864), (3.015367685, 65.982014864), (4.515367685, 65.982014864), (4.515367685, 65.482014864), (3.015367685, 62.982014864), (3.015367685, 62.482014864), (4.515367685, 62.482014864), (4.515367685, 61.982014864), (3.015367685, 59.482014864), (3.015367685, 58.982014864), (4.515367685, 58.982014864), (4.515367685, 58.482014864), (3.015367685, 55.982014864), (3.015367685, 55.482014864), (4.515367685, 55.482014864), (4.515367685, 54.982014864), (3.015367685, 52.482014864), (3.015367685, 51.982014864), (4.515367685, 51.982014864), (4.515367685, 51.482014864), (3.015367685, 48.982014864), (3.015367685, 48.482014864), (4.515367685, 48.482014864), (4.515367685, 47.982014864), (3.015367685, 45.482014864), (3.015367685, 44.982014864), (4.515367685, 44.982014864), (4.515367685, 44.482014864), (3.015367685, 41.982014864), (3.015367685, 41.482014864), (4.515367685, 41.482014864), (4.515367685, 40.982014864), (3.015367685, 38.482014864), (3.015367685, 37.982014864), (4.515367685, 37.982014864), (4.515367685, 37.482014864), (3.015367685, 34.982014864), (3.015367685, 34.482014864), (4.515367685, 34.482014864), (4.515367685, 33.982014864), (3.015367685, 31.482014864), (3.015367685, 30.982014864), (4.515367685, 30.982014864), (4.515367685, 30.482014864), (3.015367685, 27.982014864), (3.015367685, 27.482014864), (4.515367685, 27.482014864), (4.515367685, 26.982014864), (3.015367685, 24.482014864), (3.015367685, 23.982014864), (4.515367685, 23.982014864), (4.515367685, 23.482014864), (3.015367685, 20.982014864), (3.015367685, 20.482014864), (4.515367685, 20.482014864), (4.515367685, 19.982014864), (3.015367685, 17.482014864), (3.015367685, 16.982014864), (4.515367685, 16.982014864), (4.515367685, 16.482014864), (3.015367685, 13.982014864), (3.015367685, 13.482014864), (4.515367685, 13.482014864), (4.515367685, 12.982014864), (3.015367685, 10.482014864), (3.015367685, 9.982014864), (4.515367685, 9.982014864), (4.515367685, 9.482014864), (3.015367685, 6.982014864), (3.015367685, 6.482014864), (4.515367685, 6.482014864), (4.515367685, 5.982014864), (3.015367685, 3.482014864), (3.015367685, 2.982014864), (4.515367685, 2.982014864), (4.515367685, 2.482014864), (3.015367685, -0.017985136), (5.554076741, -2.217724732), align=None)
    extrude(amount=-CUT_EXTRUDE6_DEPTH, mode=Mode.SUBTRACT)

    # Sketch9 → Cut-Extrude7 (cut)
    with BuildSketch(Plane(origin=(0, 0, 0), x_dir=(-1, 0, 0), z_dir=(0, -1, 0))):
        with Locations((9.438092424, -29.5)):
            Rectangle(SKETCH9_W, SKETCH9_H)
    extrude(amount=-CUT_EXTRUDE7_DEPTH, mode=Mode.SUBTRACT)


solid = part.part
